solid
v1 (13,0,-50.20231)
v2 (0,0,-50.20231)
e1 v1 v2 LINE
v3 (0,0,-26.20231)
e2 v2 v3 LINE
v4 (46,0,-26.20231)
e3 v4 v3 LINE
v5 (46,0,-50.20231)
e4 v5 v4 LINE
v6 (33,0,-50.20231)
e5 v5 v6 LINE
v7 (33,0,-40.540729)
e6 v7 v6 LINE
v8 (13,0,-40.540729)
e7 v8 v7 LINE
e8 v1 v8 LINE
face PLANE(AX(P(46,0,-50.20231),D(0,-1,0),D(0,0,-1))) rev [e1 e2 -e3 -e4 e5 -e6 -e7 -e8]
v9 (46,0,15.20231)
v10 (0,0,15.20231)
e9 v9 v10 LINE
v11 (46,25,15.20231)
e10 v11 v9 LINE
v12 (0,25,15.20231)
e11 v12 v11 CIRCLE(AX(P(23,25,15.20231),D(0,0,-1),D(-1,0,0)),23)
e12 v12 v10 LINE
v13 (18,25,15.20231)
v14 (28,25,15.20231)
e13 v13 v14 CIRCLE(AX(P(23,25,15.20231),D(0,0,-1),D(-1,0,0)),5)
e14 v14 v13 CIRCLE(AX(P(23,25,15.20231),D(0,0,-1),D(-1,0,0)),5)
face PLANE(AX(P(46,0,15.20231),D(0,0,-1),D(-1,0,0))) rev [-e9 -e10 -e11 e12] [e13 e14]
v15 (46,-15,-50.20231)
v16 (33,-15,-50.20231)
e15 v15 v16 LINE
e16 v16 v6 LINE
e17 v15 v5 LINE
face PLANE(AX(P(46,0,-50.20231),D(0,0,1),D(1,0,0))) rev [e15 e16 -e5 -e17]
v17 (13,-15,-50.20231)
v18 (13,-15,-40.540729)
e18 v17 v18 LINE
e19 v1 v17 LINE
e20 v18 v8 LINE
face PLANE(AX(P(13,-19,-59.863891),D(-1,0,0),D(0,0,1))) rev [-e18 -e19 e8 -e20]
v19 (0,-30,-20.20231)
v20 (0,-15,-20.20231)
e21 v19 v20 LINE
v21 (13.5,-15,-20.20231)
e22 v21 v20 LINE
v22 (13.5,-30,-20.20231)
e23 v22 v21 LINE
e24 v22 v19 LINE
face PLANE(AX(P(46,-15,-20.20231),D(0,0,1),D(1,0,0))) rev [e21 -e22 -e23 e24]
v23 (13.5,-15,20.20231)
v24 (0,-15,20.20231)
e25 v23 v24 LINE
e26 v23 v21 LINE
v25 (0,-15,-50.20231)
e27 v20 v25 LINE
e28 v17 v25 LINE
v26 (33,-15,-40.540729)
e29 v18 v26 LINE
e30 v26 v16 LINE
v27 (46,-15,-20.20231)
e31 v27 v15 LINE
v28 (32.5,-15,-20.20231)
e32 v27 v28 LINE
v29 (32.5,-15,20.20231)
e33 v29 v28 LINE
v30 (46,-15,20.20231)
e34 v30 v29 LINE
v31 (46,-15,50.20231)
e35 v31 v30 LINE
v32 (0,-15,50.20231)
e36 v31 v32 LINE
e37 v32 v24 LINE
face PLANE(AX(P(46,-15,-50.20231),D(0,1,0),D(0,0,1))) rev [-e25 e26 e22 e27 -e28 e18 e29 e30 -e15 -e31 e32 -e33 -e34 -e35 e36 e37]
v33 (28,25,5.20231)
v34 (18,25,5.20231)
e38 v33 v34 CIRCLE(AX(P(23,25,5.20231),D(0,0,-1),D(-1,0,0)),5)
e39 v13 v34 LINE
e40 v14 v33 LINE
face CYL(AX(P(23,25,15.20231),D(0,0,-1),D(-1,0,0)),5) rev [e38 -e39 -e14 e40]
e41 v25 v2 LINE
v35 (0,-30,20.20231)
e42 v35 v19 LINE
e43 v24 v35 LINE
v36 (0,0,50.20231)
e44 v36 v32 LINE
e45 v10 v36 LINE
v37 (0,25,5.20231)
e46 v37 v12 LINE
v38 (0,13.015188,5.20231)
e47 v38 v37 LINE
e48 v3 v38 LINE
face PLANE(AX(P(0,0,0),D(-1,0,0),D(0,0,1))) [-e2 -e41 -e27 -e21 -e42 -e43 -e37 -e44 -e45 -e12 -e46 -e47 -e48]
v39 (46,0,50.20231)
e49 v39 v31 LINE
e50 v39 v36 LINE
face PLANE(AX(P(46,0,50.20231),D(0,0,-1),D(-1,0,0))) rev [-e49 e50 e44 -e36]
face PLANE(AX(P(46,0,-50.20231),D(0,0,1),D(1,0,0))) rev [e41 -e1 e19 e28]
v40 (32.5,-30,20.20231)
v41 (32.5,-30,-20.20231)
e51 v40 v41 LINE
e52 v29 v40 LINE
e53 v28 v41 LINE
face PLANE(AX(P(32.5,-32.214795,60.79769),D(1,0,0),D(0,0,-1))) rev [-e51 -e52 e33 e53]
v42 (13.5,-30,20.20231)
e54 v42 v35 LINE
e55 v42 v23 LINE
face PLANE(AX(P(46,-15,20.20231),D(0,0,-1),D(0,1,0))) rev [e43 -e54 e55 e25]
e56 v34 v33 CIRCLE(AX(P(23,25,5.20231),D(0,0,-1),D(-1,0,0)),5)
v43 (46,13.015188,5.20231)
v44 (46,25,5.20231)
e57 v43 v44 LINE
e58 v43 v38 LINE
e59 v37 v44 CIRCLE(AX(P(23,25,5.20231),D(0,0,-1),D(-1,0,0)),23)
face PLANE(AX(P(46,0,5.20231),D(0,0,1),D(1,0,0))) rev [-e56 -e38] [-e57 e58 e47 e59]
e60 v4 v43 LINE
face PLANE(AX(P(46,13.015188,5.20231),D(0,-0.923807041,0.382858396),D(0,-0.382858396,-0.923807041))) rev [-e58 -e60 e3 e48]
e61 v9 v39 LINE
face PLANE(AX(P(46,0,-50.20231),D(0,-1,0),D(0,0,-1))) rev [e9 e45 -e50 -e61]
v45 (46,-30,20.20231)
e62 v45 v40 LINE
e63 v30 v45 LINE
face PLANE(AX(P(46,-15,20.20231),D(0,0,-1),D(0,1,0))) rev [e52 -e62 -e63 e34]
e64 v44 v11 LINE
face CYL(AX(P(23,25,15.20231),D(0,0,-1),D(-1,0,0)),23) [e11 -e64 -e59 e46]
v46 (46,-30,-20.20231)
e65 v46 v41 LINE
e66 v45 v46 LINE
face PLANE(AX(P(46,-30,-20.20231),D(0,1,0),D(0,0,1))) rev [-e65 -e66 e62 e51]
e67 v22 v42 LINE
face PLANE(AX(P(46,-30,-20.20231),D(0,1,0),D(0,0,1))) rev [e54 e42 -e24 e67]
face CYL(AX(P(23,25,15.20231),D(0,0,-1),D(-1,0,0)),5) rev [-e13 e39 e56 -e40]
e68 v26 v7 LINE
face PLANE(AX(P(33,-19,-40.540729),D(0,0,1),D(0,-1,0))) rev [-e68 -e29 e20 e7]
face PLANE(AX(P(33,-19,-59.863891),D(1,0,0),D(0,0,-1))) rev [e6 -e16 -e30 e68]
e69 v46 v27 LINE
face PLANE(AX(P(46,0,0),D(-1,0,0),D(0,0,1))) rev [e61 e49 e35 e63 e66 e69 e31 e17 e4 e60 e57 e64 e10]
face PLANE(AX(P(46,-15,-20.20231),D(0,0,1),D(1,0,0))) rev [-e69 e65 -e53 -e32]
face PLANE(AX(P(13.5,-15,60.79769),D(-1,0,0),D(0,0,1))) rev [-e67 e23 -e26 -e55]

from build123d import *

# Parameters (mm, degrees)
BASE_BODY_DEPTH         = 46
SIDE_BLOCK_SKETCH_W     = 10
SIDE_BLOCK_SKETCH_H     = 25
SIDE_BLOCK_DEPTH        = 23
FRONT_BLOCK_DEPTH       = 23
LUG_DEPTH               = 10
LUG_EXTENSION_SKETCH_R  = 5
LUG_EXTENSION_DEPTH     = 10
PIN_HOLE_SKETCH_R       = 5
LUG_PIN_HOLE_DEPTH      = 10
SLOT_SKETCH_W           = 20
SLOT_SKETCH_H           = 19.323161221
SLOT_CUT_DEPTH          = 19
ANGLED_RELIEF_CUT_DEPTH = 81


with BuildPart() as part:
    # Base Profile Sketch → Base Body (new body)
    with BuildSketch(Plane(origin=(0, 0, 0), x_dir=(0, 0, -1), z_dir=(1, 0, 0))):
        Polygon((50.202309924, 0), (-50.202309924, 0), (-50.202309924, -15), (-20.202309924, -15), (-20.202309924, -30), (20.202309924, -30), (20.202309924, -15), (50.202309924, -15), align=None)
    extrude(amount=BASE_BODY_DEPTH)

    # Side Block Sketch → Side Block (add, symmetric)
    with BuildSketch(Plane(origin=(23, 0, 0), x_dir=(0, 0, -1), z_dir=(1, 0, 0))):
        with Locations((-10.202309924, 12.5)):
            Rectangle(SIDE_BLOCK_SKETCH_W, SIDE_BLOCK_SKETCH_H)
    extrude(amount=SIDE_BLOCK_DEPTH, both=True)

    # Front Block Sketch → Front Block (add, symmetric)
    with BuildSketch(Plane(origin=(23, 0, 0), x_dir=(0, 0, -1), z_dir=(1, 0, 0))):
        Polygon((-5.202309924, 13.015188061), (26.202309924, 0), (-5.202309924, 0), (-5.202309924, 13), align=None)
    extrude(amount=FRONT_BLOCK_DEPTH, both=True)

    # Lug Sketch → Lug (add)
    with BuildSketch(Plane(origin=(0, 0, 5.202309924), x_dir=(-1, 0, 0), z_dir=(0, 0, -1))):
        with BuildLine():
            ThreePointArc((-33, 25), (-23, 35), (-13, 25))
            Line((-13, 25), (0, 25))
            ThreePointArc((0, 25), (-23, 48), (-46, 25))
            Line((-46, 25), (-33, 25))
        make_face()
    extrude(amount=-LUG_DEPTH)

    # Lug Extension Sketch → Lug Extension (add)
    with BuildSketch(Plane(origin=(0, 0, 5.202309924), x_dir=(-1, 0, 0), z_dir=(0, 0, -1))):
        with Locations((-23, 25)):
            Circle(LUG_EXTENSION_SKETCH_R)
        with BuildLine():
            Line((-13, 25), (-33, 25))
            ThreePointArc((-33, 25), (-23, 35), (-13, 25))
        make_face()
        with BuildLine():
            ThreePointArc((-28, 25), (-23, 20), (-18, 25))
            Line((-18, 25), (-28, 25))
        make_face()
        with BuildLine():
            Line((-28, 25), (-18, 25))
            ThreePointArc((-18, 25), (-23, 30), (-28, 25))
        make_face()
    extrude(amount=-LUG_EXTENSION_DEPTH)

    # Pin Hole Sketch → Lug Pin Hole (cut)
    with BuildSketch(Plane(origin=(0, 0, 5.202309924), x_dir=(-1, 0, 0), z_dir=(0, 0, -1))):
        with Locations((-23, 25)):
            Circle(PIN_HOLE_SKETCH_R)
    extrude(amount=-LUG_PIN_HOLE_DEPTH, mode=Mode.SUBTRACT)

    # Slot Sketch → Slot Cut (cut)
    with BuildSketch(Plane(origin=(0, 0, 0), x_dir=(1, 0, 0), z_dir=(0, 1, 0))):
        with Locations((23, 50.202309924)):
            Rectangle(SLOT_SKETCH_W, SLOT_SKETCH_H)
    extrude(amount=-SLOT_CUT_DEPTH, mode=Mode.SUBTRACT)

    # Angled Cut Sketch → Angled Relief Cut (cut)
    with BuildSketch(Plane(origin=(0, 0, -20.202309924), x_dir=(-1, 0, 0), z_dir=(0, 0, -1))):
        Polygon((-23, -15), (-32.5, -15), (-32.5, -32.214795119), (-13.5, -32.214795119), (-13.5, -15), align=None)
    extrude(amount=-ANGLED_RELIEF_CUT_DEPTH, mode=Mode.SUBTRACT)


solid = part.part
